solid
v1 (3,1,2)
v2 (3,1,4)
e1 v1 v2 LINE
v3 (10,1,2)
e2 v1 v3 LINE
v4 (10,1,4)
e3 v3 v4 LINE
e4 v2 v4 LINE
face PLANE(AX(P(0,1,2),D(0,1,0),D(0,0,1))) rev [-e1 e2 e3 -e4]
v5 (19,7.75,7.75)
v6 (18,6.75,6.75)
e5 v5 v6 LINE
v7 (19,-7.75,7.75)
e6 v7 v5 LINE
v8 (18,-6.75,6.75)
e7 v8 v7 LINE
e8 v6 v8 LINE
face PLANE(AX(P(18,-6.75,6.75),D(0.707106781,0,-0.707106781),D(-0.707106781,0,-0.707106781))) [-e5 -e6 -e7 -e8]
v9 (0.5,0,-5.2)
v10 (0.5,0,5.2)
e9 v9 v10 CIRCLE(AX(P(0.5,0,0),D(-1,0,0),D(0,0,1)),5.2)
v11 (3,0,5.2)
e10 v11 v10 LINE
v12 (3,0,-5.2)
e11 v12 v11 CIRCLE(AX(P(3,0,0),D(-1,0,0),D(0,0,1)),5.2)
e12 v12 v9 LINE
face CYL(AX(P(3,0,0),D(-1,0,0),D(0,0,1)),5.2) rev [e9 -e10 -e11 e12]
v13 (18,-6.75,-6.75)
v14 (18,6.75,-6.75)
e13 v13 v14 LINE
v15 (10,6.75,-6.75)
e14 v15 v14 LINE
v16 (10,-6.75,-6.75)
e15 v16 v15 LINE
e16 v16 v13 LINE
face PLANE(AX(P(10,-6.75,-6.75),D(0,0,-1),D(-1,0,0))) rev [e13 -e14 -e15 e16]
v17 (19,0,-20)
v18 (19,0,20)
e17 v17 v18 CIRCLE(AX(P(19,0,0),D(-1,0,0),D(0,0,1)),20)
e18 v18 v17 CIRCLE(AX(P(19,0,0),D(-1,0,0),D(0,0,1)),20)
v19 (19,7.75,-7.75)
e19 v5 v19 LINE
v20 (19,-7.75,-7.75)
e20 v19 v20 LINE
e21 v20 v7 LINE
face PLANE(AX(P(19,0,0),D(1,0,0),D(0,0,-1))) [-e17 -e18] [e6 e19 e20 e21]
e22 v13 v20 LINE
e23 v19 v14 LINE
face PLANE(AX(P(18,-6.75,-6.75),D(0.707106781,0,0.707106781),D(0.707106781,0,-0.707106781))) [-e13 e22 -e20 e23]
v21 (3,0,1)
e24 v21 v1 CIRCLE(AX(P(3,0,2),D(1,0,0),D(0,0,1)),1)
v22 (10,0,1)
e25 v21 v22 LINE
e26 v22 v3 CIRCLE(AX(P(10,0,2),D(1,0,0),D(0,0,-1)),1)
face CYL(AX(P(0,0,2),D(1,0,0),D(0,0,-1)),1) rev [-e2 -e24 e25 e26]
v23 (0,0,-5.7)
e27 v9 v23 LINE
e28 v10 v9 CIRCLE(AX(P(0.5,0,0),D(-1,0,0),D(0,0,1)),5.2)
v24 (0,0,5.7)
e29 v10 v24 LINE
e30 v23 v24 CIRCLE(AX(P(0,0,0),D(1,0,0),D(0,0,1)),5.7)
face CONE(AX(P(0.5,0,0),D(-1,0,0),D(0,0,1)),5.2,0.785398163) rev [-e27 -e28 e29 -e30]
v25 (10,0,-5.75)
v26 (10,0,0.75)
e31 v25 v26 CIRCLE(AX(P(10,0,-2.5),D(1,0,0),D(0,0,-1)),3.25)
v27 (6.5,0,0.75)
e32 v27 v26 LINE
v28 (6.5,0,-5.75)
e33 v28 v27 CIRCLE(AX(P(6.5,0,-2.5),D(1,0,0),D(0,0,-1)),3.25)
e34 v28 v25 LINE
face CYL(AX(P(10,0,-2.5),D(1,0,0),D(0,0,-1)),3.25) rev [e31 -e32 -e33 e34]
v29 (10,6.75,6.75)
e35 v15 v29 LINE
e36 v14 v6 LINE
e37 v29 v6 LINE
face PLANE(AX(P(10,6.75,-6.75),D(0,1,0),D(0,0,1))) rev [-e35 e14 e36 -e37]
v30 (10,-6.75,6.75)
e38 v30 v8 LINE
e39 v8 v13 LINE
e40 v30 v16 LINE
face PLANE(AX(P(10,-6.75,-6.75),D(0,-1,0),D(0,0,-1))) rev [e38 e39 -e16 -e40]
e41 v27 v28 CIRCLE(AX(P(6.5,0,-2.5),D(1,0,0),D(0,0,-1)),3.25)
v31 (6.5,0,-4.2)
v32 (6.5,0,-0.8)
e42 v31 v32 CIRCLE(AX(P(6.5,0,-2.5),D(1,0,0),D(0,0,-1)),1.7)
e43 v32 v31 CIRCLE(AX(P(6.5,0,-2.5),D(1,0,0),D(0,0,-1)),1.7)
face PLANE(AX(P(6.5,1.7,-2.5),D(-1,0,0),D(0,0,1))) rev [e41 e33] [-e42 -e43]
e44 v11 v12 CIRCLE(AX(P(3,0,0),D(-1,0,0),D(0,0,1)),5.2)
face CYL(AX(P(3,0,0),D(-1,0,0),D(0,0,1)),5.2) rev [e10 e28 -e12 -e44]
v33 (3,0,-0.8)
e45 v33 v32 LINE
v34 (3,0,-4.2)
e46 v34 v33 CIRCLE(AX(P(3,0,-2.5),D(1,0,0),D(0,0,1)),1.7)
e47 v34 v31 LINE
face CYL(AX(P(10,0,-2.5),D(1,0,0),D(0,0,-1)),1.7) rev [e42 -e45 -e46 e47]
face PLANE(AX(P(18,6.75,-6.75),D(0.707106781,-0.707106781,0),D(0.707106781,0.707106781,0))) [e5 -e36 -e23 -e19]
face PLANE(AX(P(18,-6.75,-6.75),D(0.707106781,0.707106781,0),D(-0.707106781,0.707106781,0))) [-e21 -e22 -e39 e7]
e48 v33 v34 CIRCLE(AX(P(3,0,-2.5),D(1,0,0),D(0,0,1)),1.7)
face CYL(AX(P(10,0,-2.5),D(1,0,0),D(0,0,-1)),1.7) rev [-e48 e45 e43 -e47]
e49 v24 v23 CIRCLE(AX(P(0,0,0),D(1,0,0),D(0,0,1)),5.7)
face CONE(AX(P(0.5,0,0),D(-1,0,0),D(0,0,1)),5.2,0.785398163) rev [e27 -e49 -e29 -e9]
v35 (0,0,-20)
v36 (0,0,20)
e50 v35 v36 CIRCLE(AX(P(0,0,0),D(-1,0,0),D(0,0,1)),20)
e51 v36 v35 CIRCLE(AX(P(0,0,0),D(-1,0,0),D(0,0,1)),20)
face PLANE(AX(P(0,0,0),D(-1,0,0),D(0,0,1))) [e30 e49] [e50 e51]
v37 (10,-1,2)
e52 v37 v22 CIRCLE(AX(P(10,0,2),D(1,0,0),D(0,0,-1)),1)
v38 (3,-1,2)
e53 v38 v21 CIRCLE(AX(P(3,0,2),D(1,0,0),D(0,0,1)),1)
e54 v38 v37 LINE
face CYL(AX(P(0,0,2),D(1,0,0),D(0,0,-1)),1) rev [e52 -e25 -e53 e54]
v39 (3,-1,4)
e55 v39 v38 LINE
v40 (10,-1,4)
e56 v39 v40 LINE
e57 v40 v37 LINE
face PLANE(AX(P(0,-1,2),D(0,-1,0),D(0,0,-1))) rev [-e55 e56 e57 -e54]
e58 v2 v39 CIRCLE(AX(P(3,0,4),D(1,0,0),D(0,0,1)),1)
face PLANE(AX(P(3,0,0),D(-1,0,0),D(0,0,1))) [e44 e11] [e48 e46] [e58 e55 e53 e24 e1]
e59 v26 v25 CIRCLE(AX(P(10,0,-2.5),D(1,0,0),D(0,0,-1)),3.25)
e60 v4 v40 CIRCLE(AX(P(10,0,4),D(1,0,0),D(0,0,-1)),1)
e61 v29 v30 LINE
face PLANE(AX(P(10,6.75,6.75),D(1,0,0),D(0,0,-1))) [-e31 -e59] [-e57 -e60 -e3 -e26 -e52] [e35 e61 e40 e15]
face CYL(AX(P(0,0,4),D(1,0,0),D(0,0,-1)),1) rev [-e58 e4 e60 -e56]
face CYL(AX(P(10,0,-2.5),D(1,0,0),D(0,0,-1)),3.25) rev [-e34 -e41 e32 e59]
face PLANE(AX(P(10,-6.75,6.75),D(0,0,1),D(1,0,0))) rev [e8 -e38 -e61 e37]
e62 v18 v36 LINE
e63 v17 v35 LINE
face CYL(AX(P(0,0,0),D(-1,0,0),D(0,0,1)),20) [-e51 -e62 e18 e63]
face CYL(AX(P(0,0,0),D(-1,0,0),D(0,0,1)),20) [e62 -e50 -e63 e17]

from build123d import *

# Parameters (mm, degrees)
SKETCH1_W                                           = 19
SKETCH1_H                                           = 20
SKETCH2_W                                           = 13.5
SKETCH2_H                                           = 13.5
CUT_EXTRUDE1_DEPTH                                  = 9
CBORE_FOR_M3_HEX_SOCKET_HEAD_CAP_SCREW1_D           = 3.4
CBORE_FOR_M3_HEX_SOCKET_HEAD_CAP_SCREW1_CBORE_D     = 6.5
CBORE_FOR_M3_HEX_SOCKET_HEAD_CAP_SCREW1_CBORE_DEPTH = 3.5
CUT_EXTRUDE2_DEPTH                                  = 31
SKETCH6_R                                           = 5.2
CUT_EXTRUDE3_DEPTH                                  = 3
CHAMFER1_SIZE                                       = 0.5
CHAMFER2_SIZE                                       = 1


with BuildPart() as part:
    # Sketch1 → Revolve1 (revolve)
    with BuildSketch(Plane(origin=(0, 0, 0), x_dir=(1, 0, 0), z_dir=(0, 1, 0))):
        with Locations((9.5, -10)):
            Rectangle(SKETCH1_W, SKETCH1_H)
    revolve(axis=Axis((0, 0, 0), (1, 0, 0)))

    # Sketch2 → Cut-Extrude1 (cut)
    with BuildSketch(Plane(origin=(19, 0, 0), x_dir=(0, 0, -1), z_dir=(1, 0, 0))):
        Rectangle(SKETCH2_W, SKETCH2_H)
    extrude(amount=-CUT_EXTRUDE1_DEPTH, mode=Mode.SUBTRACT)

    # CBORE for M3 Hex Socket Head Cap Screw1 (through all)
    with Locations(Plane(origin=(10, 0, 0), x_dir=(0, 0, -1), z_dir=(1, 0, 0))):
        with Locations((2.5, 0)):
            CounterBoreHole(CBORE_FOR_M3_HEX_SOCKET_HEAD_CAP_SCREW1_D / 2, CBORE_FOR_M3_HEX_SOCKET_HEAD_CAP_SCREW1_CBORE_D / 2, CBORE_FOR_M3_HEX_SOCKET_HEAD_CAP_SCREW1_CBORE_DEPTH)

    # Sketch5 → Cut-Extrude2 (cut, through all)
    with BuildSketch(Plane(origin=(10, 0, 0), x_dir=(0, 0, -1), z_dir=(1, 0, 0))):
        with BuildLine():
            Line((-2, -1), (-4, -1))
            ThreePointArc((-4, -1), (-5, 0), (-4, 1))
            Line((-4, 1), (-2, 1))
            ThreePointArc((-2, 1), (-1, 0), (-2, -1))
        make_face()
    extrude(amount=-CUT_EXTRUDE2_DEPTH, mode=Mode.SUBTRACT)

    # Sketch6 → Cut-Extrude3 (cut)
    with BuildSketch(Plane.ZY):
        Circle(SKETCH6_R)
    extrude(amount=-CUT_EXTRUDE3_DEPTH, mode=Mode.SUBTRACT)

    # Chamfer1
    chamfer1_edges = [part.edges().sort_by_distance(p)[0] for p in [
        (0, 0, -5.2),
    ]]
    chamfer(chamfer1_edges, length=CHAMFER1_SIZE)

    # Chamfer2
    chamfer2_edges = [part.edges().sort_by_distance(p)[0] for p in [
        (19, 0, 6.75),
        (19, -6.75, 0),
        (19, 0, -6.75),
        (19, 6.75, 0),
    ]]
    chamfer(chamfer2_edges, length=CHAMFER2_SIZE)


solid = part.part
